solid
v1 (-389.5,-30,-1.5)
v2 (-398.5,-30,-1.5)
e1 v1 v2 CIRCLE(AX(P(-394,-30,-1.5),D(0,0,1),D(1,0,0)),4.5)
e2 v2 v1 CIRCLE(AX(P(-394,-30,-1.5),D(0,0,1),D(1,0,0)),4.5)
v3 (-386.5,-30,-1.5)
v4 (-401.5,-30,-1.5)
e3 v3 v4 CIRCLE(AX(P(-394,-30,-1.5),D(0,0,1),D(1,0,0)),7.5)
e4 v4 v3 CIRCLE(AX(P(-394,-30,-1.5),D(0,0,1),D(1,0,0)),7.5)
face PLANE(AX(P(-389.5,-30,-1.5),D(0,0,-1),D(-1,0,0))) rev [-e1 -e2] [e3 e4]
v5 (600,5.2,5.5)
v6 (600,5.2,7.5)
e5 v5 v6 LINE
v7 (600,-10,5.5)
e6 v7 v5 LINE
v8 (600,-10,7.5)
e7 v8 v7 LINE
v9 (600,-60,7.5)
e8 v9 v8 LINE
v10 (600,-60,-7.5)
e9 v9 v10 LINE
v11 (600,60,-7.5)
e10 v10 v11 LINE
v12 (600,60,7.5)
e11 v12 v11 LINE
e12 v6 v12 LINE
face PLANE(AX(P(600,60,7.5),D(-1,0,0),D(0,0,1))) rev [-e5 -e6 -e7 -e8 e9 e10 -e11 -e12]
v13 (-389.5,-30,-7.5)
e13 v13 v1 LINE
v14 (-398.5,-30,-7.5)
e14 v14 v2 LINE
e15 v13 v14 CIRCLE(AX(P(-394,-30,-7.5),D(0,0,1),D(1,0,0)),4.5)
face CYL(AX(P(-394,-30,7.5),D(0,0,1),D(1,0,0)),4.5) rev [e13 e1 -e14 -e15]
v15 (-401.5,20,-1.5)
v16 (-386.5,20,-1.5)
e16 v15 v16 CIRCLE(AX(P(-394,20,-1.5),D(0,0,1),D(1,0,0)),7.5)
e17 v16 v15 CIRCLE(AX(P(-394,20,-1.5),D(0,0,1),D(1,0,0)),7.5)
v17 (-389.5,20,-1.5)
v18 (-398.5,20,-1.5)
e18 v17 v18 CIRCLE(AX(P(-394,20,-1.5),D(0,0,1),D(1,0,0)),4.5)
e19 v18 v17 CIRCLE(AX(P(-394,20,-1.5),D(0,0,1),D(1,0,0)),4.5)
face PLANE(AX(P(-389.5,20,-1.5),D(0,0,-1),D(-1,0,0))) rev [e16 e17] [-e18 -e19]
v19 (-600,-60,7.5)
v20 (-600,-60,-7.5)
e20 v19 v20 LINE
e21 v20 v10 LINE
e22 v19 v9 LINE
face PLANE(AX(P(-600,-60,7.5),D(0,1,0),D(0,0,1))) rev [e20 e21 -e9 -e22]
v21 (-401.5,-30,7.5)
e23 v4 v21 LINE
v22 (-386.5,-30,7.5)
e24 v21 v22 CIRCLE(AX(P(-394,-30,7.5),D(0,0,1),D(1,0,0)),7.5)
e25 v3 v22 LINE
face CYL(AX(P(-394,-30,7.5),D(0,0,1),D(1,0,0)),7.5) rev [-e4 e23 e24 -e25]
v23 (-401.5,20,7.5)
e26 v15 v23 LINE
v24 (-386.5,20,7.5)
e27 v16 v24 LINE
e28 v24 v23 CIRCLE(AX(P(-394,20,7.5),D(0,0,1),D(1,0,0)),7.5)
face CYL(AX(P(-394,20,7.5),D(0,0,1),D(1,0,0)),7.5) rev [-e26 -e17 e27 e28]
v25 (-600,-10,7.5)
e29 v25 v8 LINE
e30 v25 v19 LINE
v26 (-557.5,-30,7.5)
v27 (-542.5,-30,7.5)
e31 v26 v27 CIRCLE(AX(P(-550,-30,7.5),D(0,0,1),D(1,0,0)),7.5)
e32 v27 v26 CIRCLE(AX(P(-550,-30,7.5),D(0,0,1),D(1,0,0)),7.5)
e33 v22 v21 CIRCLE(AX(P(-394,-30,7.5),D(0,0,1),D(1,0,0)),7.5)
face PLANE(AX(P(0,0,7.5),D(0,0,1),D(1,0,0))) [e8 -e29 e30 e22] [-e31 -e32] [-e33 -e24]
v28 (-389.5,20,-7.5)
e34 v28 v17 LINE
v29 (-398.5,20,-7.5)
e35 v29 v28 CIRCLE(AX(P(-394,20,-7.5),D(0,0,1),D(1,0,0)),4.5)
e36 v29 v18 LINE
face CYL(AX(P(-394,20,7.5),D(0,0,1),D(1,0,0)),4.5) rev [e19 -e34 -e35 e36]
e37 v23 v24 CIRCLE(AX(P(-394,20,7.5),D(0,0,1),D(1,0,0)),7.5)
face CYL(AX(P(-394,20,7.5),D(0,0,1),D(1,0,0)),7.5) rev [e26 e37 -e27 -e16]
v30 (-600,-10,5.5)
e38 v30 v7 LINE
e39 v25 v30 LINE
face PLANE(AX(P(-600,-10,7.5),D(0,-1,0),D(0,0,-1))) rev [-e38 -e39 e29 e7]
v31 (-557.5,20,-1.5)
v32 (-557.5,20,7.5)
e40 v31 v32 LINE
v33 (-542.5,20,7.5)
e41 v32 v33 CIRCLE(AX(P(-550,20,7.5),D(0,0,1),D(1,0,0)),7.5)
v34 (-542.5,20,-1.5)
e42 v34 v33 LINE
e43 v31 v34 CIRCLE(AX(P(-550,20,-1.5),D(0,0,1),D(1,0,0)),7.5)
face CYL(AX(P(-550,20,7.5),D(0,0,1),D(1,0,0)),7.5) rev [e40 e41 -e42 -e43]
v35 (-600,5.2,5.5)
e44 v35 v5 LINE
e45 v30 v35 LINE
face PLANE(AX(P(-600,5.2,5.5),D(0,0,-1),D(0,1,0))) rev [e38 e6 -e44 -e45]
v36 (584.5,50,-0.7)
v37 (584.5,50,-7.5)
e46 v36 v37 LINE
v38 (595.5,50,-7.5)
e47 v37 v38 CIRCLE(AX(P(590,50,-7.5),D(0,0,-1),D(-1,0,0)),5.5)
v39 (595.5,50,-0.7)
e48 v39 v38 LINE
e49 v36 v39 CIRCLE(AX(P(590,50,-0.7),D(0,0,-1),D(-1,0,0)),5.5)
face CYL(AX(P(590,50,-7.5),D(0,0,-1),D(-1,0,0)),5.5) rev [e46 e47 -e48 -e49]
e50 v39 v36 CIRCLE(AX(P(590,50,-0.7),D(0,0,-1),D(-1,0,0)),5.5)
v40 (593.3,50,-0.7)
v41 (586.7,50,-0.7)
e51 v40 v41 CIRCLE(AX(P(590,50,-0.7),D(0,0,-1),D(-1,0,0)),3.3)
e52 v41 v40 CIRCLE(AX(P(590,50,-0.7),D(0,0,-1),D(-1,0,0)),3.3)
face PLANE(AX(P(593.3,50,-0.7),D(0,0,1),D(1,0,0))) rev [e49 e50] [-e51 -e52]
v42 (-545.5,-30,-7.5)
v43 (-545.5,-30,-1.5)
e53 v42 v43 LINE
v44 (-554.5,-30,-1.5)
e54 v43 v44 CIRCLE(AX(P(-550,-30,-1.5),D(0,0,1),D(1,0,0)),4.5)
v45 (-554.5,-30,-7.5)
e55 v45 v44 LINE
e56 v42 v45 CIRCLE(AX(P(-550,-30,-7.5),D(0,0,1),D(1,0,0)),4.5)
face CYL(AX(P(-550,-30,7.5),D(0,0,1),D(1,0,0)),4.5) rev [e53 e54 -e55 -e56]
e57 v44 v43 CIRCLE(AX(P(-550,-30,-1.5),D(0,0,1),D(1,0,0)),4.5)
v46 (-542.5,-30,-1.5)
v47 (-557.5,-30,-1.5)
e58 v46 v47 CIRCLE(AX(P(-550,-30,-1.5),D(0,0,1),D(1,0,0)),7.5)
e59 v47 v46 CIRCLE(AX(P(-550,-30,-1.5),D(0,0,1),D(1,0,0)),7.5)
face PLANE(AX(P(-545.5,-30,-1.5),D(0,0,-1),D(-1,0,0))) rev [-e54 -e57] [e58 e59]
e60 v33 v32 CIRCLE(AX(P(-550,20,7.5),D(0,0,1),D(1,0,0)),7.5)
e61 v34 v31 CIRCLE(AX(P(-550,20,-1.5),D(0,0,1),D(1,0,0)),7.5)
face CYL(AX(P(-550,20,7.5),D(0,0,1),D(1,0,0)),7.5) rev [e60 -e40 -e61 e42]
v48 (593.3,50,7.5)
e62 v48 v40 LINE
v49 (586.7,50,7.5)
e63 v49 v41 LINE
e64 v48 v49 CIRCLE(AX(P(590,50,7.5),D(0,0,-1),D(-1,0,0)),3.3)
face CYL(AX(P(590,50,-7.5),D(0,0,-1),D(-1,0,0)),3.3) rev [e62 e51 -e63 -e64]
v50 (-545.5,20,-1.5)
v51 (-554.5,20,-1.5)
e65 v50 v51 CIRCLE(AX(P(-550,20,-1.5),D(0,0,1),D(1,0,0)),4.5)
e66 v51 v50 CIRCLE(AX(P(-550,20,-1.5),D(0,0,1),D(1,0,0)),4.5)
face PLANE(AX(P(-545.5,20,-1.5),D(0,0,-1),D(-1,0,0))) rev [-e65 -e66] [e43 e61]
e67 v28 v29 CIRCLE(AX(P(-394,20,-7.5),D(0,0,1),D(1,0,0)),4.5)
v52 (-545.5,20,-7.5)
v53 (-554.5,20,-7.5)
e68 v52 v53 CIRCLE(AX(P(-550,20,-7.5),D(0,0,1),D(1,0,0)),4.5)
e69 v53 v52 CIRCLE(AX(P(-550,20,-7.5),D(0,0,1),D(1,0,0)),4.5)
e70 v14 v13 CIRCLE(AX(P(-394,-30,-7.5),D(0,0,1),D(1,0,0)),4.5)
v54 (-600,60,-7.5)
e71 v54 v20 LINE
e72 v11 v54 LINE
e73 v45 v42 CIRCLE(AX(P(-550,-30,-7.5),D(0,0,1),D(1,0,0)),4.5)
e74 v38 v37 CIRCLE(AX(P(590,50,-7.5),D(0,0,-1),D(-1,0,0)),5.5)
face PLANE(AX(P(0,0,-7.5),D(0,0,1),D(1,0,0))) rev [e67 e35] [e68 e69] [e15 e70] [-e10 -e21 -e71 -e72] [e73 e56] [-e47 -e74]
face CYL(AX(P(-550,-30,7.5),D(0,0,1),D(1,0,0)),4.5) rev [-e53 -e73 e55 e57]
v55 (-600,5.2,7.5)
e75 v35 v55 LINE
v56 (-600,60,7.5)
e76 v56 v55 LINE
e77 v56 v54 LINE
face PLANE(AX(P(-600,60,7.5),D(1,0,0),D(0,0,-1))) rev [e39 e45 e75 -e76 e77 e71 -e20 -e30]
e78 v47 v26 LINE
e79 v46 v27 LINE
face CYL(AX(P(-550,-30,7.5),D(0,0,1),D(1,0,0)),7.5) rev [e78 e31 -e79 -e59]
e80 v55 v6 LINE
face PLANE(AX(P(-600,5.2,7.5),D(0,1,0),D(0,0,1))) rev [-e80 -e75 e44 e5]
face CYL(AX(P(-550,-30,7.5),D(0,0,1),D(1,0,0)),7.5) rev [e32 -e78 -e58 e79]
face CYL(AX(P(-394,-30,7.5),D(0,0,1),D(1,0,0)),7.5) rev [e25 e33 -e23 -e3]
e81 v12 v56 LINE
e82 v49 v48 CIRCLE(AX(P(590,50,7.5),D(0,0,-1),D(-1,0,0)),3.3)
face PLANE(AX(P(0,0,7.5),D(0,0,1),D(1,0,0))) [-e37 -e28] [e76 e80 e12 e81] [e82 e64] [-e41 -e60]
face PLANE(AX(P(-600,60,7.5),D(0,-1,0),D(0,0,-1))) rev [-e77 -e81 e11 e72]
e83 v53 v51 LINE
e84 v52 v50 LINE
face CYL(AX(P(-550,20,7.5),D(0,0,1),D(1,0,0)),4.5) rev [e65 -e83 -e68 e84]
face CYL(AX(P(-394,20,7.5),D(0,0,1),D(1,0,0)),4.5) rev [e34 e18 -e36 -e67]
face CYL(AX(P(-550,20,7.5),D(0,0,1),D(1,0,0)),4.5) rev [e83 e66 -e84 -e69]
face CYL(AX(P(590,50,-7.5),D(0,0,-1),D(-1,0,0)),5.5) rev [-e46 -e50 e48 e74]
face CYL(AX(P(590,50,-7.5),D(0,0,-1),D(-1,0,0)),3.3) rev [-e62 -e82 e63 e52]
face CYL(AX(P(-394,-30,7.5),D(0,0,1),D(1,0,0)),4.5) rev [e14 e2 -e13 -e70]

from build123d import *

# Parameters (mm, degrees)
SKETCH_1_W                  = 1200
SKETCH_1_H                  = 120
EXTRUDE_1_DEPTH             = 7.5
HOLE_WIZARD_3_D             = 6.6
HOLE_WIZARD_3_CBORE_D       = 11
HOLE_WIZARD_3_CBORE_DEPTH   = 6.8
HOLE_WIZARD_3_2_D           = 9
HOLE_WIZARD_3_2_CBORE_D     = 15
HOLE_WIZARD_3_2_CBORE_DEPTH = 9
SKETCH_7_W                  = 2
SKETCH_7_H                  = 15.2
CUT_EXTRUDE_1_DEPTH         = 1202.5224717


with BuildPart() as part:
    # 草图1 → 凸台-拉伸1 (new, symmetric)
    with BuildSketch(Plane.XY):
        Rectangle(SKETCH_1_W, SKETCH_1_H)
    extrude(amount=EXTRUDE_1_DEPTH, both=True)

    # Hole Wizard 3 (through all)
    with Locations(Plane(origin=(590, 50, -7.5), x_dir=(-1, 0, 0), z_dir=(0, 0, -1))):
        with Locations((0, 0)):
            CounterBoreHole(HOLE_WIZARD_3_D / 2, HOLE_WIZARD_3_CBORE_D / 2, HOLE_WIZARD_3_CBORE_DEPTH)

    # Hole Wizard 3 2 (through all)
    with Locations(Plane(origin=(-550, 20, 7.5), x_dir=(1, 0, 0), z_dir=(0, 0, 1))):
        with Locations((0, 0), (156, 0), (156, -50), (0, -50)):
            CounterBoreHole(HOLE_WIZARD_3_2_D / 2, HOLE_WIZARD_3_2_CBORE_D / 2, HOLE_WIZARD_3_2_CBORE_DEPTH)

    # 草图7 → 切除-拉伸1 (cut, through all)
    with BuildSketch(Plane(origin=(600, 0, 0), x_dir=(0, 0, -1), z_dir=(1, 0, 0))):
        with Locations((-6.5, -2.4)):
            Rectangle(SKETCH_7_W, SKETCH_7_H)
    extrude(amount=-CUT_EXTRUDE_1_DEPTH, mode=Mode.SUBTRACT)


solid = part.part
